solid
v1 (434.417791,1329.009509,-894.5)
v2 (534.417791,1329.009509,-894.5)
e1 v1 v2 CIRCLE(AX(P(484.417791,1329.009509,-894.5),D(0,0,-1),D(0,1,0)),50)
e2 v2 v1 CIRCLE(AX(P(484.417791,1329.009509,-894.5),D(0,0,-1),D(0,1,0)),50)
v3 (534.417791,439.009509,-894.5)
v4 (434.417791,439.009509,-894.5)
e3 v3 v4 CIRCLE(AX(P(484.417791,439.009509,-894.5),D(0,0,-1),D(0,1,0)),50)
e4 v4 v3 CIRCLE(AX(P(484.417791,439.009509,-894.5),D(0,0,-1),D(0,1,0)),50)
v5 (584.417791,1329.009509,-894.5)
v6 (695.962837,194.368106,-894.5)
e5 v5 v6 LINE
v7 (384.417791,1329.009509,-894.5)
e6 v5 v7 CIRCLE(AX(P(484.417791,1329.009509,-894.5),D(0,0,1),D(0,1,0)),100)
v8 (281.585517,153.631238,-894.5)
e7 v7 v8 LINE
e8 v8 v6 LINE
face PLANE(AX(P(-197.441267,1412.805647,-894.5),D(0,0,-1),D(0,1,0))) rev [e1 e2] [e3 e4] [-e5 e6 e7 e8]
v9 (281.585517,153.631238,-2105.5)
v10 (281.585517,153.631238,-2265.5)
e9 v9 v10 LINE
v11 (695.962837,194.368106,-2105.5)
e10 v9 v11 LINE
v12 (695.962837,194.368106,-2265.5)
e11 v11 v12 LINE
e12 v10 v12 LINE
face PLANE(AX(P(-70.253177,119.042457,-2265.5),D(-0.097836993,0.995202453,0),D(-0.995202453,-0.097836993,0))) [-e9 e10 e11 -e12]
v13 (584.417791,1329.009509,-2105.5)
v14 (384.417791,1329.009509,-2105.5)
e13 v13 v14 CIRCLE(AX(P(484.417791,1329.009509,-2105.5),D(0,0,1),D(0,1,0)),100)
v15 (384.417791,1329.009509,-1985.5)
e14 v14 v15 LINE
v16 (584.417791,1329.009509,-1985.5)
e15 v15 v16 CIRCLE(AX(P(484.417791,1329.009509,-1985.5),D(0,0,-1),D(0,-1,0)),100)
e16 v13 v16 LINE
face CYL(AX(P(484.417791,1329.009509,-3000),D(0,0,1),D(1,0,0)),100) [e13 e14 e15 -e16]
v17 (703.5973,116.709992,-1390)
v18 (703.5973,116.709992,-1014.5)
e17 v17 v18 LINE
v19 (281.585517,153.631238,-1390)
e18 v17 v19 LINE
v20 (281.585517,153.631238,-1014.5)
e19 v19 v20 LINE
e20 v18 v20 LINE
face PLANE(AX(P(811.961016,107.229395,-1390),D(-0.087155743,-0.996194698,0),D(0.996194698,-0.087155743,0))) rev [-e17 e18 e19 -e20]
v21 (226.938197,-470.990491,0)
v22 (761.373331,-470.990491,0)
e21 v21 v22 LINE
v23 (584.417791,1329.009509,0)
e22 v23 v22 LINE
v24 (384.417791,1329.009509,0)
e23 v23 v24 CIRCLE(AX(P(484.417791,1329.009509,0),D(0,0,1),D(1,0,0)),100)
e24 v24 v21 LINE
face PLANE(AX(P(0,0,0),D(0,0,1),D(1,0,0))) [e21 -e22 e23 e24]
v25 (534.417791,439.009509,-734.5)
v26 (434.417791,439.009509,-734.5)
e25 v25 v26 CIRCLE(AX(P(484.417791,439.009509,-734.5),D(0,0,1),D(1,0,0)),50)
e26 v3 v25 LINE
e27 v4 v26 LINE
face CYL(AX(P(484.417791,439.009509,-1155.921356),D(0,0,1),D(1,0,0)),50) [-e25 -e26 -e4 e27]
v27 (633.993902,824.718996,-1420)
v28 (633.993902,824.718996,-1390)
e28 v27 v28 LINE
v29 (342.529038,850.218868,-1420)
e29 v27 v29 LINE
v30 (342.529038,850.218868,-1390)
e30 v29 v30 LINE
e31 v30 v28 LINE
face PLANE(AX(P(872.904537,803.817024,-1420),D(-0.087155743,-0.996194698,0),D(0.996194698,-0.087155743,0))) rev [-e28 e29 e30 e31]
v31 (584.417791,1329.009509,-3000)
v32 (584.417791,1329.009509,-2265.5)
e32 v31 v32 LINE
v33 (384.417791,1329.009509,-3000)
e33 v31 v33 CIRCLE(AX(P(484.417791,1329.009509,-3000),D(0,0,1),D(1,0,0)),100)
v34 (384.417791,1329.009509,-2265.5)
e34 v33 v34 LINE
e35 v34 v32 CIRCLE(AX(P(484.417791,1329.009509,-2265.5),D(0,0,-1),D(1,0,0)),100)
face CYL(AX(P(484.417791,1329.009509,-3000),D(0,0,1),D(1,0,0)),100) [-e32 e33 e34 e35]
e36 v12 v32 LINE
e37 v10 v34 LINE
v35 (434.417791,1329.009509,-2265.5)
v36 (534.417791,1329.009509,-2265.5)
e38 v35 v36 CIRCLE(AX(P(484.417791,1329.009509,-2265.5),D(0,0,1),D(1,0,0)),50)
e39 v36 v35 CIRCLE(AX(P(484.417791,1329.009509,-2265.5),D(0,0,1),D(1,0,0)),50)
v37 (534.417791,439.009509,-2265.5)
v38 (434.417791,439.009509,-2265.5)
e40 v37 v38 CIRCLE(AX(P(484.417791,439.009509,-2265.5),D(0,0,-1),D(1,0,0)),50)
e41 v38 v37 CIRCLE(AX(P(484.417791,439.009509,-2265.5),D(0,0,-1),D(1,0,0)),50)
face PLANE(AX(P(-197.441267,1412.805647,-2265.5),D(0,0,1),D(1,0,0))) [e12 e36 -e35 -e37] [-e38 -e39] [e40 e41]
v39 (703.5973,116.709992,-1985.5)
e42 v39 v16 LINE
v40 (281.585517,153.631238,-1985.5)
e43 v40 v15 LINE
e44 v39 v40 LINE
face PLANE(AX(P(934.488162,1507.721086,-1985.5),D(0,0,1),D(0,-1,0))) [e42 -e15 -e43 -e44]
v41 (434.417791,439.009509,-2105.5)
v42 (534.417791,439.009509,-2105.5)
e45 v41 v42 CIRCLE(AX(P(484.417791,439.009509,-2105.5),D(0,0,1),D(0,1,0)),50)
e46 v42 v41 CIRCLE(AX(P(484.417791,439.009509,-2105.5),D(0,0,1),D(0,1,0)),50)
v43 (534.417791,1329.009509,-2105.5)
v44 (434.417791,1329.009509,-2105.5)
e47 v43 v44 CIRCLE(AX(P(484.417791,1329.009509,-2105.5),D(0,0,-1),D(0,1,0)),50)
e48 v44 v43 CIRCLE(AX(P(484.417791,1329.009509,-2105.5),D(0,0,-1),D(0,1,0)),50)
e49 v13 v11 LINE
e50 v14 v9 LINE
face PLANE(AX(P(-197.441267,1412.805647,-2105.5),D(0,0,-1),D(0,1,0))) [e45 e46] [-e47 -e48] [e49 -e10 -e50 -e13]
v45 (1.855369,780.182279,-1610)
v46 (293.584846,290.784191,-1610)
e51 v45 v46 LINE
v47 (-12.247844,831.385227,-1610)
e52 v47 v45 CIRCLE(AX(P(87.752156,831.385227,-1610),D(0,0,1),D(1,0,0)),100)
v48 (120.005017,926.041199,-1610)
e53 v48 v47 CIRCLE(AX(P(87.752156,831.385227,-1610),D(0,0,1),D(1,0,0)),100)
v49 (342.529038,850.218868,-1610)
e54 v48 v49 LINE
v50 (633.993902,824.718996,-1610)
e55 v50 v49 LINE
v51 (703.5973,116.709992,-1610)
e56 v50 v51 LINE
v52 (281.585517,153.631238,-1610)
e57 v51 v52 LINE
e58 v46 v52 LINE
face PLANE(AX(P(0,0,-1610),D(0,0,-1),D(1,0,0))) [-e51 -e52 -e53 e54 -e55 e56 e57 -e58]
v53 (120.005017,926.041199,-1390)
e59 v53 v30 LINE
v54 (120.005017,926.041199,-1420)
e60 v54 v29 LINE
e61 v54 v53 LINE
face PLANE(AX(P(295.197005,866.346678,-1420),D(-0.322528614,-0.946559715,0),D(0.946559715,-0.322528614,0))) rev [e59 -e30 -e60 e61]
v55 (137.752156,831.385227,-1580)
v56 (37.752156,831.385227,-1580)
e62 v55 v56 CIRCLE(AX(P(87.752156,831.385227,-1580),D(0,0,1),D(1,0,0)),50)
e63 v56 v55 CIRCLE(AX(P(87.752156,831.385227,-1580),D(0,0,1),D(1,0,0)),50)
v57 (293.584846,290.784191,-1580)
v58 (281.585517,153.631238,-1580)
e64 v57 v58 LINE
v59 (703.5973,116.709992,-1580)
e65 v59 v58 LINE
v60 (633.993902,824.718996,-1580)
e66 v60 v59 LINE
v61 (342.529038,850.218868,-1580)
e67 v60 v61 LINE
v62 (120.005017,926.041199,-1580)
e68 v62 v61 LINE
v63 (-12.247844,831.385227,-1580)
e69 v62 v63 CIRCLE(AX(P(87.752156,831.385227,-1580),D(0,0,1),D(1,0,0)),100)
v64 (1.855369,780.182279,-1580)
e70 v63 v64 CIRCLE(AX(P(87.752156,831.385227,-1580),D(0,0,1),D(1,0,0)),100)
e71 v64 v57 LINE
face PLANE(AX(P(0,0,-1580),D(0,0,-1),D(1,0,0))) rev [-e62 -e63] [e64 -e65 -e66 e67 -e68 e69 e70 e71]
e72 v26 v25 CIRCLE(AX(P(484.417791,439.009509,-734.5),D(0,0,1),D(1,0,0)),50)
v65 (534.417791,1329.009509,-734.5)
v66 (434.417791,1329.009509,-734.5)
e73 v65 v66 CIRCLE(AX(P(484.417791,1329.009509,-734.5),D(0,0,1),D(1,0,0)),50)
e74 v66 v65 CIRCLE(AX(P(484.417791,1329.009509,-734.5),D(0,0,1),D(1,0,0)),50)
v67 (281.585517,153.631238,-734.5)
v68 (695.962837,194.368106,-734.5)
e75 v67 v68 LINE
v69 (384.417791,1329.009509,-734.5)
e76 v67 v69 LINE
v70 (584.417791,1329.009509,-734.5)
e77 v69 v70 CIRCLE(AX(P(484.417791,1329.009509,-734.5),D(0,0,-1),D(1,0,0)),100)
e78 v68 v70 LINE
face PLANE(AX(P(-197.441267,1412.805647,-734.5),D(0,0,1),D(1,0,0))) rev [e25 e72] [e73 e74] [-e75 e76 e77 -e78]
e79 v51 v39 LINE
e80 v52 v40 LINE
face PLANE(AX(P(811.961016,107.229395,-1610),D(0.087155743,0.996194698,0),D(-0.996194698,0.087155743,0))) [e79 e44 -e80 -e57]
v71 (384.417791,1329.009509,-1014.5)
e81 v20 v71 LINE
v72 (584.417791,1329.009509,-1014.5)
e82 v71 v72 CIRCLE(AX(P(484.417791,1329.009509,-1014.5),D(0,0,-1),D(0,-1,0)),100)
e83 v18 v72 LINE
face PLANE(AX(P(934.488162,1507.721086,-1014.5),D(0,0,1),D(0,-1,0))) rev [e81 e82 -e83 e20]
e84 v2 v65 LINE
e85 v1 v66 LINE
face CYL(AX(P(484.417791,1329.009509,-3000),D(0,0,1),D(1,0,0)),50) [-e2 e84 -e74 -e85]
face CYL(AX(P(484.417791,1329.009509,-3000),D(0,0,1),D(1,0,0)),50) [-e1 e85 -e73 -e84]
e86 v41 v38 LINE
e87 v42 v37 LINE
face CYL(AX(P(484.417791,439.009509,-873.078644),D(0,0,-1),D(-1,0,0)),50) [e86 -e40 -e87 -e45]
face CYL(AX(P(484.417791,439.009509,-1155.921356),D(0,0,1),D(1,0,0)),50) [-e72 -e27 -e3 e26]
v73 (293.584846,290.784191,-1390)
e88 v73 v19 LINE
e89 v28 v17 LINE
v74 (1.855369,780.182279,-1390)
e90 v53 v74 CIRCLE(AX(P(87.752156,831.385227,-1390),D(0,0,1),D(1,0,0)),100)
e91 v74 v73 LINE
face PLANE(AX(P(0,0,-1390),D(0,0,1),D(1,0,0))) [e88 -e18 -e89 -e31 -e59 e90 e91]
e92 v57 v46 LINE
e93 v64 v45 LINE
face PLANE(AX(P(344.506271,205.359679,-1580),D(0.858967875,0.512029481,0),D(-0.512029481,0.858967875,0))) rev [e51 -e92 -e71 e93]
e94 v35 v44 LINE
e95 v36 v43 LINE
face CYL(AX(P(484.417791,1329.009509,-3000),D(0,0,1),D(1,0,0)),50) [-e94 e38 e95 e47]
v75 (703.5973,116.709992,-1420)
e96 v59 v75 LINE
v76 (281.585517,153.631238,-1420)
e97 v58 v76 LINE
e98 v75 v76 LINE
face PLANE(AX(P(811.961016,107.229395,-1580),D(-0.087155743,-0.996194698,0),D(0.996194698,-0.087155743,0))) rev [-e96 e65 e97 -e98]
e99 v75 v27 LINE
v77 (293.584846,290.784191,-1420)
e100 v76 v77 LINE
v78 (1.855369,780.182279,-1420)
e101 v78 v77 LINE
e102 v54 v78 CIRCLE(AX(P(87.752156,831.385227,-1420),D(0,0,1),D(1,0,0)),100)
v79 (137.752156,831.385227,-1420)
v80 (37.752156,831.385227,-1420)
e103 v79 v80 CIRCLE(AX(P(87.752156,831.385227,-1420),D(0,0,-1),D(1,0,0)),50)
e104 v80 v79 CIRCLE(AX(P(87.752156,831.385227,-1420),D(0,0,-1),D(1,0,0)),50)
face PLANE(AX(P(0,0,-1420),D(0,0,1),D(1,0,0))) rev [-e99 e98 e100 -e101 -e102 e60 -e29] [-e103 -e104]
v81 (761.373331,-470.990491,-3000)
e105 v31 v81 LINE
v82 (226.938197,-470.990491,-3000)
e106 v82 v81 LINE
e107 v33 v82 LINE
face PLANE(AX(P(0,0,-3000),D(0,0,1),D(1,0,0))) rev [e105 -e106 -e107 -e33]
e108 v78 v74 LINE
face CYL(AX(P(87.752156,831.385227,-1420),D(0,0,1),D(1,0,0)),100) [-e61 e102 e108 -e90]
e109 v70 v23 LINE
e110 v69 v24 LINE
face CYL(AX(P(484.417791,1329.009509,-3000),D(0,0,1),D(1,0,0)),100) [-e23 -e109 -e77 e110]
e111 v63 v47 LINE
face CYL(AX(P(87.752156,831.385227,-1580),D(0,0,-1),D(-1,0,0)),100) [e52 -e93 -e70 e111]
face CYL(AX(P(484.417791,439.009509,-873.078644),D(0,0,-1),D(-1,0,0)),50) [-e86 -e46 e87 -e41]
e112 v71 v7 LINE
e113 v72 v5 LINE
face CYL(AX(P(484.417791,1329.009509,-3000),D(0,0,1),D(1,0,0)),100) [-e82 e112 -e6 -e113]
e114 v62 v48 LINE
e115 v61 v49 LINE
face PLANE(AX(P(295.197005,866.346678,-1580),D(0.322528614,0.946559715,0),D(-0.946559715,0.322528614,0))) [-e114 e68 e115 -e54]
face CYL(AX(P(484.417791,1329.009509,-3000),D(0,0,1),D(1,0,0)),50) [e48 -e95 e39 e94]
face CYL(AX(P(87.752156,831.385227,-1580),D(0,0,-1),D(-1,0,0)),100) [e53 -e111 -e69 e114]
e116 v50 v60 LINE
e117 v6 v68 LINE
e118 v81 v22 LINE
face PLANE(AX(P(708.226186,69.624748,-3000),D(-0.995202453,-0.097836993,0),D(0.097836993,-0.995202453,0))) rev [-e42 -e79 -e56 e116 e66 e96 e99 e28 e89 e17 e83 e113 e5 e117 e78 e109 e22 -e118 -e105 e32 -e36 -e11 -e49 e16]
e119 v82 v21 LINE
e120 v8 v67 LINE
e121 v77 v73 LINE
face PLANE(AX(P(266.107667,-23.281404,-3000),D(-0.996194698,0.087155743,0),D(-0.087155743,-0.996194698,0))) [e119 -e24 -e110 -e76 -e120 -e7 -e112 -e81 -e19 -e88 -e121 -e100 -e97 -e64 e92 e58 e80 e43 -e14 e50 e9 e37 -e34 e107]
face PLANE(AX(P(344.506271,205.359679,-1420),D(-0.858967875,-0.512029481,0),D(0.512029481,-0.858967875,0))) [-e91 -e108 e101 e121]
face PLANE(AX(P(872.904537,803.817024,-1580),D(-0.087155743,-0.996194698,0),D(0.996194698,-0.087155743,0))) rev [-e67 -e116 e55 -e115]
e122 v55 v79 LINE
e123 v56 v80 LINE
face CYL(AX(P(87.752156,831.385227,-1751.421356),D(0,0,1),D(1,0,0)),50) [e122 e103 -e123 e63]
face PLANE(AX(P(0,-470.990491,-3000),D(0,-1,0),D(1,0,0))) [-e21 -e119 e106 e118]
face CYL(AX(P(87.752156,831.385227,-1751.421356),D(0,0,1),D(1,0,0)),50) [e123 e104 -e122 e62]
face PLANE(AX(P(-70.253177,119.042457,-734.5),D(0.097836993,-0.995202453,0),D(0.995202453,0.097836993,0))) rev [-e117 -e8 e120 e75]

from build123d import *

# Parameters (mm, degrees)
SKETCH_1_5_R            = 100
SKETCH_1_5_R_2          = 50
BOSS_EXTRUDE1_DEPTH     = 3000
BOSS_EXTRUDE2_START     = -1390
SKETCH_1_4_R            = 100
SKETCH_1_4_R_2          = 50
BOSS_EXTRUDE2_DEPTH     = 30
SKETCH2_W               = 160
SKETCH2_H               = 1300
CUT_EXTRUDE1_DEPTH      = 3372.499629859
BOSS_EXTRUDE3_REACH     = 3411.07
SKETCH_1_5_2_R          = 50
SKETCH3_W               = 375.5
SKETCH3_H               = 1405.841341372
CUT_EXTRUDE2_DEPTH      = 3370.634545963
CUT_EXTRUDE3_DEPTH      = 3370.634545963
CUT_EXTRUDE4_DEPTH      = 3370.634545963
CUT_EXTRUDE4_DEPTH_BACK = 3370.634545963
SKETCH5_W               = 421.157999818
SKETCH5_H               = 173.673401987
SKETCH6_R               = 50
BOSS_EXTRUDE4_DEPTH     = 220
SKETCH7_R               = 50
BOSS_EXTRUDE5_DEPTH     = 1014.5


with BuildPart() as part:
    # Sketch 1_5 → Boss-Extrude1 (new body)
    # profile 1 of 3: a face of its own
    with BuildSketch(Plane.XY):
        with BuildLine():
            ThreePointArc((584.417791302, 1329.00950863), (484.417791302, 1229.00950863), (384.417791302, 1329.00950863))
            Line((384.417791302, 1329.00950863), (342.529038033, 850.218867874))
            Line((342.529038033, 850.218867874), (293.584845824, 290.784191003))
            Line((293.584845824, 290.784191003), (226.938196955, -470.99049137))
            Line((226.938196955, -470.99049137), (761.373330839, -470.99049137))
            Line((761.373330839, -470.99049137), (584.417791302, 1329.00950863))
        make_face()
    # profile 2 of 3: a face of its own
    with BuildSketch(Plane.XY):
        with Locations((484.417791302, 1329.00950863)):
            Circle(SKETCH_1_5_R)
        with Locations((484.417791302, 1329.00950863)):
            Circle(SKETCH_1_5_R_2, mode=Mode.SUBTRACT)
    # profile 3 of 3: a face of its own
    with BuildSketch(Plane.XY):
        with Locations((484.417791302, 1329.00950863)):
            Circle(SKETCH_1_5_R_2)
    extrude(amount=-BOSS_EXTRUDE1_DEPTH)

    # 草图1<4> → Boss-Extrude2 (add)
    # profile 1 of 2: a face of its own
    with BuildSketch(Plane.XY.offset(BOSS_EXTRUDE2_START)):
        with BuildLine():
            Line((293.584845824, 290.784191003), (342.529038033, 850.218867874))
            Line((342.529038033, 850.218867874), (120.005017386, 926.041198717))
            ThreePointArc((120.005017386, 926.041198717), (169.070315555, 889.586231815), (187.752156036, 831.385227248))
            ThreePointArc((187.752156036, 831.385227248), (114.3070167, 734.975479945), (1.855368534, 780.182279122))
            Line((1.855368534, 780.182279122), (293.584845824, 290.784191003))
        make_face()
    # profile 2 of 2: a face of its own
    with BuildSketch(Plane.XY.offset(BOSS_EXTRUDE2_START)):
        with Locations((87.752156036, 831.385227248)):
            Circle(SKETCH_1_4_R)
        with Locations((87.752156036, 831.385227248)):
            Circle(SKETCH_1_4_R_2, mode=Mode.SUBTRACT)
    boss_extrude2 = extrude(amount=-BOSS_EXTRUDE2_DEPTH)

    # Mirror1: Boss-Extrude2 across plane
    add(boss_extrude2.mirror(Plane.XY.offset(-1500)))

    # Sketch2 → Cut-Extrude1 (cut, symmetric)
    with BuildSketch(Plane(origin=(708.226185615, 69.624748217, 0), x_dir=(0, 0, -1), z_dir=(0.9952024531915172, 0.09783699280735358, 0))):
        with Locations((814.5, 775.344705163)):
            Rectangle(SKETCH2_W, SKETCH2_H)
    cut_extrude1 = extrude(amount=CUT_EXTRUDE1_DEPTH, both=True, mode=Mode.SUBTRACT)

    # Mirror2: Cut-Extrude1 across plane
    add(cut_extrude1.mirror(Plane.XY.offset(-1500)), mode=Mode.SUBTRACT)

    # Sketch 1_5 2 → Boss-Extrude3 (add, up to next)
    with BuildSketch(Plane.XY, mode=Mode.PRIVATE) as boss_extrude3_sk1:
        with Locations((484.417791302, 1329.00950863)):
            Circle(SKETCH_1_5_2_R)
    boss_extrude3_tool1 = extrude(boss_extrude3_sk1.sketch, amount=-BOSS_EXTRUDE3_REACH, mode=Mode.PRIVATE) - part.part
    add(boss_extrude3_tool1.solids().sort_by_distance((484.417791, 1329.009509, 0))[0])
    add(boss_extrude3_tool1.solids().sort_by_distance((484.417791, 1329.009509, 0))[1])

    # Sketch3 → Cut-Extrude2 (cut, symmetric)
    with BuildSketch(Plane(origin=(266.107666648, -23.281404109, 0), x_dir=(0, 0, 1), z_dir=(-0.9961946980917458, 0.0871557427476561, 0))):
        with Locations((-1202.25, 880.509090801)):
            Rectangle(SKETCH3_W, SKETCH3_H)
    cut_extrude2 = extrude(amount=CUT_EXTRUDE2_DEPTH, both=True, mode=Mode.SUBTRACT)

    # Mirror3: Cut-Extrude2 across plane
    add(cut_extrude2.mirror(Plane.XY.offset(-1500)), mode=Mode.SUBTRACT)

    # Sketch4 → Cut-Extrude3 (cut, through all)
    with BuildSketch(Plane(origin=(266.107666648, -23.281404109, 0), x_dir=(0, 0, 1), z_dir=(-0.9961946980917458, 0.0871557427476561, 0))):
        Polygon((-1672.587737226, 1602.596949433), (-1327.412262774, 1602.596949433), (-1327.412262774, 876.836901116), (-1420, 876.836901116), (-1420, 177.588420115), (-1580, 177.588420115), (-1580, 876.836901116), (-1672.587737226, 876.836901116), align=None)
    extrude(amount=-CUT_EXTRUDE3_DEPTH, mode=Mode.SUBTRACT)


with BuildPart() as cut_extrude3_piece_1:
    # of the separate pieces the step leaves, piece 1, a body of its own (cut_extrude3_pieces)
    add(part.part.solids().sort_by_distance((384.417791302, 1329.00950863, -3000))[0])

    # Sketch6 → Boss-Extrude4 (add)
    with BuildSketch(Plane.XY.offset(-1390)):
        with Locations((87.752156036, 831.385227248)):
            Circle(SKETCH6_R)
    extrude(amount=-BOSS_EXTRUDE4_DEPTH)

    # Sketch7 → Boss-Extrude5 (add)
    with BuildSketch(Plane.XY):
        with Locations((484.417791302, 439.00950863)):
            Circle(SKETCH7_R)
    boss_extrude5 = extrude(amount=-BOSS_EXTRUDE5_DEPTH)

    # Mirror4: Boss-Extrude5 across plane
    add(boss_extrude5.mirror(Plane.XY.offset(-1500)))


with BuildPart() as cut_extrude3_piece_2:
    # of the separate pieces the step leaves, piece 2, a body of its own (cut_extrude3_pieces)
    add(part.part.solids().sort_by_distance((385.937016001, 1346.374326397, -1390))[0])

    # Sketch5 → Cut-Extrude4 (cut, two sides: drawn at the far end of the back side and taken through both)
    with BuildSketch(Plane(origin=(266.107666648, -23.281404109, 0), x_dir=(0, 0, 1), z_dir=(-0.9961946980917458, 0.0871557427476561, 0)).offset(-CUT_EXTRUDE4_DEPTH_BACK)):
        with Locations((-1476.119907227, 1348.970668805)):
            Rectangle(SKETCH5_W, SKETCH5_H)
    extrude(amount=CUT_EXTRUDE4_DEPTH + CUT_EXTRUDE4_DEPTH_BACK, mode=Mode.SUBTRACT)


solid = cut_extrude3_piece_1.part
